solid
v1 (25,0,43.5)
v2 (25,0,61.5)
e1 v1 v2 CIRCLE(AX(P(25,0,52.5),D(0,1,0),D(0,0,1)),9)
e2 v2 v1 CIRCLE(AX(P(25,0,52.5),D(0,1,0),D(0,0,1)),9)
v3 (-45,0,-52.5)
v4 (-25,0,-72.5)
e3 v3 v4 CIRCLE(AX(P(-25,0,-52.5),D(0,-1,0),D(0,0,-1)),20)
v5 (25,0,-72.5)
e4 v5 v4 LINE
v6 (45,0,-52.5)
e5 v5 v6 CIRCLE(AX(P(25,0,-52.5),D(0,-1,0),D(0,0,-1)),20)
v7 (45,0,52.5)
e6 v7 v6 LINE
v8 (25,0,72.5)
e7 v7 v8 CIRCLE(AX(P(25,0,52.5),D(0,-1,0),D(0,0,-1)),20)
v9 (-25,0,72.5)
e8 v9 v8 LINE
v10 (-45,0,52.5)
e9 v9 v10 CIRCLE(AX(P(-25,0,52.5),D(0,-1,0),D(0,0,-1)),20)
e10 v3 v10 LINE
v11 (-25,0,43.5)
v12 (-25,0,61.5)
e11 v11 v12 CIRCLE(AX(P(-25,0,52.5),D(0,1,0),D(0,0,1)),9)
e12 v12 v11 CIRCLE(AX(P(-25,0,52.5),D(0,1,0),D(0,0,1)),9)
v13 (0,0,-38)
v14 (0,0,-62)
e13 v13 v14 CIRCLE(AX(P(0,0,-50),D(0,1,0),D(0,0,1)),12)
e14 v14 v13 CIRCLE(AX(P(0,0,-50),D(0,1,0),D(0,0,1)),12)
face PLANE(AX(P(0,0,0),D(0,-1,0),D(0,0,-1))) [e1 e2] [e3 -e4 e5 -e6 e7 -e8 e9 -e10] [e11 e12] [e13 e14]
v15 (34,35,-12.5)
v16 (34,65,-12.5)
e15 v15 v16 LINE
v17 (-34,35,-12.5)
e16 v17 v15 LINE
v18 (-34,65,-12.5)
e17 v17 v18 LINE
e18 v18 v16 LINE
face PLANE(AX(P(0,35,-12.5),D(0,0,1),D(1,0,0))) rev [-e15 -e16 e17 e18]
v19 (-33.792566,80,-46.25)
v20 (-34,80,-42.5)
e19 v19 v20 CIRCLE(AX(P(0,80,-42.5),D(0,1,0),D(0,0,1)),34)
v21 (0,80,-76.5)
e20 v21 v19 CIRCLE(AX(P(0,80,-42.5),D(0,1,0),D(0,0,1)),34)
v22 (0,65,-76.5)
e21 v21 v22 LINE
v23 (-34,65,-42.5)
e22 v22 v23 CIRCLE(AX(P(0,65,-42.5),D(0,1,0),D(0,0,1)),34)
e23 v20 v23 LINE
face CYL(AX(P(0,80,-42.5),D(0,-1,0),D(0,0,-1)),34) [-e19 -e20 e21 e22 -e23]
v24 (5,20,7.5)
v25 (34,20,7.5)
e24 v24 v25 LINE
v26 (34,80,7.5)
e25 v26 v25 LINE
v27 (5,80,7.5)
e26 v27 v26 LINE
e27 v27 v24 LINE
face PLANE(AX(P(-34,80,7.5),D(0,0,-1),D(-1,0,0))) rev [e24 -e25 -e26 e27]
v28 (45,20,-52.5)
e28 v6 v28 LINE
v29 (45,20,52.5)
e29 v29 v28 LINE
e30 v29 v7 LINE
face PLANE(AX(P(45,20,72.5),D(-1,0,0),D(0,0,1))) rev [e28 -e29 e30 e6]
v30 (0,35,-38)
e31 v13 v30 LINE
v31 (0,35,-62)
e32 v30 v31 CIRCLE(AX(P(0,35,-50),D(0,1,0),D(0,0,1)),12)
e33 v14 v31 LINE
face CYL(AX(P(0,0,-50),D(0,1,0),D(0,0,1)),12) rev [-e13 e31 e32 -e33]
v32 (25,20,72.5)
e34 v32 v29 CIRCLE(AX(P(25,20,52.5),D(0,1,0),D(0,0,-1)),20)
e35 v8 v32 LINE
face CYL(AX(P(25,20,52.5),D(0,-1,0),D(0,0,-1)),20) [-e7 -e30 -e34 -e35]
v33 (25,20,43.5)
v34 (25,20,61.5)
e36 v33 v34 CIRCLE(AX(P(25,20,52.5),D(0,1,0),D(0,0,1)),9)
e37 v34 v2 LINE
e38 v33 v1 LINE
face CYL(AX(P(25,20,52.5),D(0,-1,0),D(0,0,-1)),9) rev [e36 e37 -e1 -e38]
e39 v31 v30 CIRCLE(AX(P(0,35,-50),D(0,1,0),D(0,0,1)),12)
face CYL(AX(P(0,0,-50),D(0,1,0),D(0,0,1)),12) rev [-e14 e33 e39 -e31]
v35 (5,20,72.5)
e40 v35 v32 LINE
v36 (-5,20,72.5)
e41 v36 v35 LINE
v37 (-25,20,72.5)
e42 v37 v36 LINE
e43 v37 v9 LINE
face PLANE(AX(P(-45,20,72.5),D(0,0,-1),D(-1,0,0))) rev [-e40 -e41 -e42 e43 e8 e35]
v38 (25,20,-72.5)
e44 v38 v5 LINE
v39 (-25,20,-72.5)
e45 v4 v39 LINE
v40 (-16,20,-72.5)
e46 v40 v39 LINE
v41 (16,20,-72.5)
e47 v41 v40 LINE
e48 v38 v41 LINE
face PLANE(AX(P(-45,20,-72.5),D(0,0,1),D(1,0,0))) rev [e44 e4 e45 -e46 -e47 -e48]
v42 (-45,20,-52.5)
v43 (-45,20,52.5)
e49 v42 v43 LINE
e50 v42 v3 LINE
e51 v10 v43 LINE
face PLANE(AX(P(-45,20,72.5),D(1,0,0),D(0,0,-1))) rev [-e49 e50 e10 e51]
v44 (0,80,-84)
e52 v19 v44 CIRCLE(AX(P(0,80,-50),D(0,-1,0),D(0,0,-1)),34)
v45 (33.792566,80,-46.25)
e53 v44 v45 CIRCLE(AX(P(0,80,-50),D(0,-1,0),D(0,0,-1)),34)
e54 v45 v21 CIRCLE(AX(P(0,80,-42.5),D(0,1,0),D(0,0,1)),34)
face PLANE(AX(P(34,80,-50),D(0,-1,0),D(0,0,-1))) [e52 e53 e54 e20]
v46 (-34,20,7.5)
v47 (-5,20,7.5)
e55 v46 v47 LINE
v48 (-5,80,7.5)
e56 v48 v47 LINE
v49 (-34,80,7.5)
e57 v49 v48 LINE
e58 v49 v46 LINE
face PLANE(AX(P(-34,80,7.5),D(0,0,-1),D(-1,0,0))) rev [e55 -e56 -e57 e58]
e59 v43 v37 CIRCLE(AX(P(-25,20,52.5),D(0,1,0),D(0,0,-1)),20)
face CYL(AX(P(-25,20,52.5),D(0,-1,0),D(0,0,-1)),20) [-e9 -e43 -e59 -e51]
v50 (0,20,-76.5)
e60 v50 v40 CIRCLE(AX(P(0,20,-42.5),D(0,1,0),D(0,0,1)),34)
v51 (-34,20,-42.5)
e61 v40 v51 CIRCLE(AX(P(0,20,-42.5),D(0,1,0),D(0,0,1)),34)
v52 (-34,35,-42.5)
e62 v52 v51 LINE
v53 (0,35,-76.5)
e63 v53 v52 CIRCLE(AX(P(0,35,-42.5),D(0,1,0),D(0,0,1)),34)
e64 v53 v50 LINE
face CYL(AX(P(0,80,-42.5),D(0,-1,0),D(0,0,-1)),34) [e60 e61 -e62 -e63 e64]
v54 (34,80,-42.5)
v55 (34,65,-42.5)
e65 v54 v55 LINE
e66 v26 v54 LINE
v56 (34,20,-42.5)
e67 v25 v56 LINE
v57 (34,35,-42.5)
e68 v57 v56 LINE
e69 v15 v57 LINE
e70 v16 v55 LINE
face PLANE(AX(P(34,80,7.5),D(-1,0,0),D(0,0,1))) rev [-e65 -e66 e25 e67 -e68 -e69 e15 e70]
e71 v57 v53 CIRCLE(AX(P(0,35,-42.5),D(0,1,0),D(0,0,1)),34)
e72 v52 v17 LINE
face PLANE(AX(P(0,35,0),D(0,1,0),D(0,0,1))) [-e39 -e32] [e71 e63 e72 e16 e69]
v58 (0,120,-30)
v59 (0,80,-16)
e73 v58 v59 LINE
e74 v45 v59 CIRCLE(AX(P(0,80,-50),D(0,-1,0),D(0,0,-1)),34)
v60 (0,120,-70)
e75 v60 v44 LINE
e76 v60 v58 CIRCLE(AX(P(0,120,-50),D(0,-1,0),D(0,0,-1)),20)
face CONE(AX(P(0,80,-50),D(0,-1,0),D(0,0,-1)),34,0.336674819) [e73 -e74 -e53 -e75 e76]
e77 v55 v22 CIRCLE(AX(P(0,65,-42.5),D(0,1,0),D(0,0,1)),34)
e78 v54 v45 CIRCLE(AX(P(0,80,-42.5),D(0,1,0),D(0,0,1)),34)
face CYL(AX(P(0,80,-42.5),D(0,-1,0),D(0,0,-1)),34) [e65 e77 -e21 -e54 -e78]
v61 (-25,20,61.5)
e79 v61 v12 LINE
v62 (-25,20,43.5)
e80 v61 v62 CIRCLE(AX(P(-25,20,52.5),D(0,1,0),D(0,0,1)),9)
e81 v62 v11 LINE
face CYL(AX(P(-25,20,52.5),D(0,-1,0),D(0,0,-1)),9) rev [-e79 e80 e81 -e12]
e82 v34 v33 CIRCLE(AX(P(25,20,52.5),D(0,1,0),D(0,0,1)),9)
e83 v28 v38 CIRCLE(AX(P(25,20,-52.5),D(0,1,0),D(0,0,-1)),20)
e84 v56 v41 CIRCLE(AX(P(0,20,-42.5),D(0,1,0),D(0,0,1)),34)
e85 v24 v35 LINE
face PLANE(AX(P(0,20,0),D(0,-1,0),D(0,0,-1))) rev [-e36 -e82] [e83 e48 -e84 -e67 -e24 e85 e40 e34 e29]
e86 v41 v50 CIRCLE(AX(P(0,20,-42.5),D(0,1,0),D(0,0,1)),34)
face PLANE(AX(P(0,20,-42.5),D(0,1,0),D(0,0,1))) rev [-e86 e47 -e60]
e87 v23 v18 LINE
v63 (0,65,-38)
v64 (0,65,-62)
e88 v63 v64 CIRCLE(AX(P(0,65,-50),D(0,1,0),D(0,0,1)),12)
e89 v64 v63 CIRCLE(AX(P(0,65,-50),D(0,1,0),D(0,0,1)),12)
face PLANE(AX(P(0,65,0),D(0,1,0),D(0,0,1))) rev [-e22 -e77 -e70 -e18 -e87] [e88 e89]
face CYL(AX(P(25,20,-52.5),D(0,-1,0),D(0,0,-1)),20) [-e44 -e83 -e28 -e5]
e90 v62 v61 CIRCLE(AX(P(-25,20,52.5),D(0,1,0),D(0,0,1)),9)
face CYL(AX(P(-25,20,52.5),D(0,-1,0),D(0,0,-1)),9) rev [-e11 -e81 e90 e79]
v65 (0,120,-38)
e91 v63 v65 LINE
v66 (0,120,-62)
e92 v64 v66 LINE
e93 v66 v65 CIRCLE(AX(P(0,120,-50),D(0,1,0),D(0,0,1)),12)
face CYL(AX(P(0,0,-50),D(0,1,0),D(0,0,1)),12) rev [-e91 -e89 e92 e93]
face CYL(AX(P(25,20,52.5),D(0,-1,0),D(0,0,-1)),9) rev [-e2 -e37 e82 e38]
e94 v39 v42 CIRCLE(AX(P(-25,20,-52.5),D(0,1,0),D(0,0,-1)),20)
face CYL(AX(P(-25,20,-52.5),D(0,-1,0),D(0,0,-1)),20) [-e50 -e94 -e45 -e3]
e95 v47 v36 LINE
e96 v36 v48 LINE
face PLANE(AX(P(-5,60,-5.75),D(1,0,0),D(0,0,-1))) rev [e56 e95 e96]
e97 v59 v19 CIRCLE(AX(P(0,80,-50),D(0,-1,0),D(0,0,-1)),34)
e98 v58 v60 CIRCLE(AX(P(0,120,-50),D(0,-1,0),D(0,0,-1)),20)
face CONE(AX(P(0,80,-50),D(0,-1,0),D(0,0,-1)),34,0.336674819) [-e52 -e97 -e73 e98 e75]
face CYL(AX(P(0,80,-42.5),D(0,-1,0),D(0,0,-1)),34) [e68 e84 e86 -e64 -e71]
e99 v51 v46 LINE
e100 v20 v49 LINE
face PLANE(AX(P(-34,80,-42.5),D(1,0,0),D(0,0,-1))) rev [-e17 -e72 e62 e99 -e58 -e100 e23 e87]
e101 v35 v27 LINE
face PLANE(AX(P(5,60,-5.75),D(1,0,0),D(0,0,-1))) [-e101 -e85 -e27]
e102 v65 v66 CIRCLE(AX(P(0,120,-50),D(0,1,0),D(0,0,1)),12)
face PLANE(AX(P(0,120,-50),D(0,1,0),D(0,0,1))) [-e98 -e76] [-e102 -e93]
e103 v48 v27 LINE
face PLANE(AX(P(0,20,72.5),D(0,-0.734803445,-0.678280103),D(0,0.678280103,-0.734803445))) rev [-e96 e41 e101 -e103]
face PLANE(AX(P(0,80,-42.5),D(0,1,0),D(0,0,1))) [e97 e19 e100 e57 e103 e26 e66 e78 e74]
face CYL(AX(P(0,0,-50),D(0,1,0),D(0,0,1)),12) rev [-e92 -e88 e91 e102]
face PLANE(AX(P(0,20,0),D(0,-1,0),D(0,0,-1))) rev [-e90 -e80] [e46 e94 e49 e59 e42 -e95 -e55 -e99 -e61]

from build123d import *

# Parameters (mm, degrees)
BASE_PLATE_SKETCH_W       = 90
BASE_PLATE_SKETCH_H       = 145
BASE_PLATE_SKETCH_R       = 9
BASE_PLATE_DEPTH          = 20
BASE_CORNER_FILLETS_R20_R = 20
UPRIGHT_BLOCK_DEPTH       = 60
SIDE_START                = -45
SIDE_SLOT_DEPTH           = 30
CONE_BORE_SKETCH_R        = 12
CONE_BORE_24_DEPTH        = 154.235113469
SUPPORT_RIB_10MM_REACH    = 155.235
SUPPORT_RIB_SKETCH_WALL_W = 396.929257004
SUPPORT_RIB_SKETCH_WALL_H = 10


with BuildPart() as part:
    # Base Plate Sketch → Base Plate (new body)
    with BuildSketch(Plane(origin=(0, 0, 0), x_dir=(1, 0, 0), z_dir=(0, 1, 0))):
        Rectangle(BASE_PLATE_SKETCH_W, BASE_PLATE_SKETCH_H)
        with Locations(Location((-25, -52.5, 0), (0, 0, 270))):
            Circle(BASE_PLATE_SKETCH_R, mode=Mode.SUBTRACT)
        with Locations(Location((25, -52.5, 0), (0, 0, 270))):
            Circle(BASE_PLATE_SKETCH_R, mode=Mode.SUBTRACT)
    extrude(amount=BASE_PLATE_DEPTH)

    # Base Corner Fillets R20
    base_corner_fillets_r20_edges = [part.edges().sort_by_distance(p)[0] for p in [
        (-45, 10, -72.5),
        (45, 10, -72.5),
        (45, 10, 72.5),
        (-45, 10, 72.5),
    ]]
    fillet(base_corner_fillets_r20_edges, radius=BASE_CORNER_FILLETS_R20_R)

    # Upright Block Sketch → Upright Block (add)
    with BuildSketch(Plane(origin=(0, 20, 0), x_dir=(1, 0, 0), z_dir=(0, 1, 0))):
        with BuildLine():
            Line((-34, -7.5), (34, -7.5))
            Line((34, -7.5), (34, 42.5))
            ThreePointArc((34, 42.5), (0, 76.5), (-34, 42.5))
            Line((-34, 42.5), (-34, -7.5))
        make_face()
    extrude(amount=UPRIGHT_BLOCK_DEPTH)

    # Side Slot Sketch → Side Slot (cut)
    with BuildSketch(Plane(origin=(0, 80, 0), x_dir=(1, 0, 0), z_dir=(0, 1, 0)).offset(SIDE_START)):
        with BuildLine():
            Line((-34, 42.5), (-34, 12.5))
            Line((-34, 12.5), (34, 12.5))
            Line((34, 12.5), (34, 42.5))
            ThreePointArc((34, 42.5), (0, 76.5), (-34, 42.5))
        make_face()
    extrude(amount=SIDE_SLOT_DEPTH, mode=Mode.SUBTRACT)

    # Cone Boss Profile → Cone Boss (revolve)
    with BuildSketch(Plane.XY.offset(-50), mode=Mode.PRIVATE) as cone_boss_sk:
        Polygon((0, 80), (0, 120), (20, 120), (34, 80), align=None)
    revolve(cone_boss_sk.sketch.rotate(Axis((0, 80, -50), (0, 1, 0)), 90), axis=Axis((0, 80, -50), (0, 1, 0)))

    # Cone Bore Sketch → Cone Bore Ø24 (cut, through all)
    with BuildSketch(Plane(origin=(0, 120, 0), x_dir=(1, 0, 0), z_dir=(0, 1, 0))):
        with Locations(Location((0, 50, 0), (0, 0, 270))):
            Circle(CONE_BORE_SKETCH_R)
    extrude(amount=-CONE_BORE_24_DEPTH, mode=Mode.SUBTRACT)

    # Support Rib Sketch wall → Support Rib 10mm (add, up to next)
    with BuildSketch(Plane(origin=(0, 50, 40), x_dir=(0, 0.678280102733, -0.734803444627), z_dir=(0, 0.734803444627, 0.678280102733)), mode=Mode.PRIVATE) as support_rib_10mm_sk1:
        Rectangle(SUPPORT_RIB_SKETCH_WALL_W, SUPPORT_RIB_SKETCH_WALL_H)
    support_rib_10mm_tool1 = extrude(support_rib_10mm_sk1.sketch, amount=-SUPPORT_RIB_10MM_REACH, mode=Mode.PRIVATE) - part.part
    add(support_rib_10mm_tool1.solids().sort_by_distance((0, 50, 40))[0])


solid = part.part
